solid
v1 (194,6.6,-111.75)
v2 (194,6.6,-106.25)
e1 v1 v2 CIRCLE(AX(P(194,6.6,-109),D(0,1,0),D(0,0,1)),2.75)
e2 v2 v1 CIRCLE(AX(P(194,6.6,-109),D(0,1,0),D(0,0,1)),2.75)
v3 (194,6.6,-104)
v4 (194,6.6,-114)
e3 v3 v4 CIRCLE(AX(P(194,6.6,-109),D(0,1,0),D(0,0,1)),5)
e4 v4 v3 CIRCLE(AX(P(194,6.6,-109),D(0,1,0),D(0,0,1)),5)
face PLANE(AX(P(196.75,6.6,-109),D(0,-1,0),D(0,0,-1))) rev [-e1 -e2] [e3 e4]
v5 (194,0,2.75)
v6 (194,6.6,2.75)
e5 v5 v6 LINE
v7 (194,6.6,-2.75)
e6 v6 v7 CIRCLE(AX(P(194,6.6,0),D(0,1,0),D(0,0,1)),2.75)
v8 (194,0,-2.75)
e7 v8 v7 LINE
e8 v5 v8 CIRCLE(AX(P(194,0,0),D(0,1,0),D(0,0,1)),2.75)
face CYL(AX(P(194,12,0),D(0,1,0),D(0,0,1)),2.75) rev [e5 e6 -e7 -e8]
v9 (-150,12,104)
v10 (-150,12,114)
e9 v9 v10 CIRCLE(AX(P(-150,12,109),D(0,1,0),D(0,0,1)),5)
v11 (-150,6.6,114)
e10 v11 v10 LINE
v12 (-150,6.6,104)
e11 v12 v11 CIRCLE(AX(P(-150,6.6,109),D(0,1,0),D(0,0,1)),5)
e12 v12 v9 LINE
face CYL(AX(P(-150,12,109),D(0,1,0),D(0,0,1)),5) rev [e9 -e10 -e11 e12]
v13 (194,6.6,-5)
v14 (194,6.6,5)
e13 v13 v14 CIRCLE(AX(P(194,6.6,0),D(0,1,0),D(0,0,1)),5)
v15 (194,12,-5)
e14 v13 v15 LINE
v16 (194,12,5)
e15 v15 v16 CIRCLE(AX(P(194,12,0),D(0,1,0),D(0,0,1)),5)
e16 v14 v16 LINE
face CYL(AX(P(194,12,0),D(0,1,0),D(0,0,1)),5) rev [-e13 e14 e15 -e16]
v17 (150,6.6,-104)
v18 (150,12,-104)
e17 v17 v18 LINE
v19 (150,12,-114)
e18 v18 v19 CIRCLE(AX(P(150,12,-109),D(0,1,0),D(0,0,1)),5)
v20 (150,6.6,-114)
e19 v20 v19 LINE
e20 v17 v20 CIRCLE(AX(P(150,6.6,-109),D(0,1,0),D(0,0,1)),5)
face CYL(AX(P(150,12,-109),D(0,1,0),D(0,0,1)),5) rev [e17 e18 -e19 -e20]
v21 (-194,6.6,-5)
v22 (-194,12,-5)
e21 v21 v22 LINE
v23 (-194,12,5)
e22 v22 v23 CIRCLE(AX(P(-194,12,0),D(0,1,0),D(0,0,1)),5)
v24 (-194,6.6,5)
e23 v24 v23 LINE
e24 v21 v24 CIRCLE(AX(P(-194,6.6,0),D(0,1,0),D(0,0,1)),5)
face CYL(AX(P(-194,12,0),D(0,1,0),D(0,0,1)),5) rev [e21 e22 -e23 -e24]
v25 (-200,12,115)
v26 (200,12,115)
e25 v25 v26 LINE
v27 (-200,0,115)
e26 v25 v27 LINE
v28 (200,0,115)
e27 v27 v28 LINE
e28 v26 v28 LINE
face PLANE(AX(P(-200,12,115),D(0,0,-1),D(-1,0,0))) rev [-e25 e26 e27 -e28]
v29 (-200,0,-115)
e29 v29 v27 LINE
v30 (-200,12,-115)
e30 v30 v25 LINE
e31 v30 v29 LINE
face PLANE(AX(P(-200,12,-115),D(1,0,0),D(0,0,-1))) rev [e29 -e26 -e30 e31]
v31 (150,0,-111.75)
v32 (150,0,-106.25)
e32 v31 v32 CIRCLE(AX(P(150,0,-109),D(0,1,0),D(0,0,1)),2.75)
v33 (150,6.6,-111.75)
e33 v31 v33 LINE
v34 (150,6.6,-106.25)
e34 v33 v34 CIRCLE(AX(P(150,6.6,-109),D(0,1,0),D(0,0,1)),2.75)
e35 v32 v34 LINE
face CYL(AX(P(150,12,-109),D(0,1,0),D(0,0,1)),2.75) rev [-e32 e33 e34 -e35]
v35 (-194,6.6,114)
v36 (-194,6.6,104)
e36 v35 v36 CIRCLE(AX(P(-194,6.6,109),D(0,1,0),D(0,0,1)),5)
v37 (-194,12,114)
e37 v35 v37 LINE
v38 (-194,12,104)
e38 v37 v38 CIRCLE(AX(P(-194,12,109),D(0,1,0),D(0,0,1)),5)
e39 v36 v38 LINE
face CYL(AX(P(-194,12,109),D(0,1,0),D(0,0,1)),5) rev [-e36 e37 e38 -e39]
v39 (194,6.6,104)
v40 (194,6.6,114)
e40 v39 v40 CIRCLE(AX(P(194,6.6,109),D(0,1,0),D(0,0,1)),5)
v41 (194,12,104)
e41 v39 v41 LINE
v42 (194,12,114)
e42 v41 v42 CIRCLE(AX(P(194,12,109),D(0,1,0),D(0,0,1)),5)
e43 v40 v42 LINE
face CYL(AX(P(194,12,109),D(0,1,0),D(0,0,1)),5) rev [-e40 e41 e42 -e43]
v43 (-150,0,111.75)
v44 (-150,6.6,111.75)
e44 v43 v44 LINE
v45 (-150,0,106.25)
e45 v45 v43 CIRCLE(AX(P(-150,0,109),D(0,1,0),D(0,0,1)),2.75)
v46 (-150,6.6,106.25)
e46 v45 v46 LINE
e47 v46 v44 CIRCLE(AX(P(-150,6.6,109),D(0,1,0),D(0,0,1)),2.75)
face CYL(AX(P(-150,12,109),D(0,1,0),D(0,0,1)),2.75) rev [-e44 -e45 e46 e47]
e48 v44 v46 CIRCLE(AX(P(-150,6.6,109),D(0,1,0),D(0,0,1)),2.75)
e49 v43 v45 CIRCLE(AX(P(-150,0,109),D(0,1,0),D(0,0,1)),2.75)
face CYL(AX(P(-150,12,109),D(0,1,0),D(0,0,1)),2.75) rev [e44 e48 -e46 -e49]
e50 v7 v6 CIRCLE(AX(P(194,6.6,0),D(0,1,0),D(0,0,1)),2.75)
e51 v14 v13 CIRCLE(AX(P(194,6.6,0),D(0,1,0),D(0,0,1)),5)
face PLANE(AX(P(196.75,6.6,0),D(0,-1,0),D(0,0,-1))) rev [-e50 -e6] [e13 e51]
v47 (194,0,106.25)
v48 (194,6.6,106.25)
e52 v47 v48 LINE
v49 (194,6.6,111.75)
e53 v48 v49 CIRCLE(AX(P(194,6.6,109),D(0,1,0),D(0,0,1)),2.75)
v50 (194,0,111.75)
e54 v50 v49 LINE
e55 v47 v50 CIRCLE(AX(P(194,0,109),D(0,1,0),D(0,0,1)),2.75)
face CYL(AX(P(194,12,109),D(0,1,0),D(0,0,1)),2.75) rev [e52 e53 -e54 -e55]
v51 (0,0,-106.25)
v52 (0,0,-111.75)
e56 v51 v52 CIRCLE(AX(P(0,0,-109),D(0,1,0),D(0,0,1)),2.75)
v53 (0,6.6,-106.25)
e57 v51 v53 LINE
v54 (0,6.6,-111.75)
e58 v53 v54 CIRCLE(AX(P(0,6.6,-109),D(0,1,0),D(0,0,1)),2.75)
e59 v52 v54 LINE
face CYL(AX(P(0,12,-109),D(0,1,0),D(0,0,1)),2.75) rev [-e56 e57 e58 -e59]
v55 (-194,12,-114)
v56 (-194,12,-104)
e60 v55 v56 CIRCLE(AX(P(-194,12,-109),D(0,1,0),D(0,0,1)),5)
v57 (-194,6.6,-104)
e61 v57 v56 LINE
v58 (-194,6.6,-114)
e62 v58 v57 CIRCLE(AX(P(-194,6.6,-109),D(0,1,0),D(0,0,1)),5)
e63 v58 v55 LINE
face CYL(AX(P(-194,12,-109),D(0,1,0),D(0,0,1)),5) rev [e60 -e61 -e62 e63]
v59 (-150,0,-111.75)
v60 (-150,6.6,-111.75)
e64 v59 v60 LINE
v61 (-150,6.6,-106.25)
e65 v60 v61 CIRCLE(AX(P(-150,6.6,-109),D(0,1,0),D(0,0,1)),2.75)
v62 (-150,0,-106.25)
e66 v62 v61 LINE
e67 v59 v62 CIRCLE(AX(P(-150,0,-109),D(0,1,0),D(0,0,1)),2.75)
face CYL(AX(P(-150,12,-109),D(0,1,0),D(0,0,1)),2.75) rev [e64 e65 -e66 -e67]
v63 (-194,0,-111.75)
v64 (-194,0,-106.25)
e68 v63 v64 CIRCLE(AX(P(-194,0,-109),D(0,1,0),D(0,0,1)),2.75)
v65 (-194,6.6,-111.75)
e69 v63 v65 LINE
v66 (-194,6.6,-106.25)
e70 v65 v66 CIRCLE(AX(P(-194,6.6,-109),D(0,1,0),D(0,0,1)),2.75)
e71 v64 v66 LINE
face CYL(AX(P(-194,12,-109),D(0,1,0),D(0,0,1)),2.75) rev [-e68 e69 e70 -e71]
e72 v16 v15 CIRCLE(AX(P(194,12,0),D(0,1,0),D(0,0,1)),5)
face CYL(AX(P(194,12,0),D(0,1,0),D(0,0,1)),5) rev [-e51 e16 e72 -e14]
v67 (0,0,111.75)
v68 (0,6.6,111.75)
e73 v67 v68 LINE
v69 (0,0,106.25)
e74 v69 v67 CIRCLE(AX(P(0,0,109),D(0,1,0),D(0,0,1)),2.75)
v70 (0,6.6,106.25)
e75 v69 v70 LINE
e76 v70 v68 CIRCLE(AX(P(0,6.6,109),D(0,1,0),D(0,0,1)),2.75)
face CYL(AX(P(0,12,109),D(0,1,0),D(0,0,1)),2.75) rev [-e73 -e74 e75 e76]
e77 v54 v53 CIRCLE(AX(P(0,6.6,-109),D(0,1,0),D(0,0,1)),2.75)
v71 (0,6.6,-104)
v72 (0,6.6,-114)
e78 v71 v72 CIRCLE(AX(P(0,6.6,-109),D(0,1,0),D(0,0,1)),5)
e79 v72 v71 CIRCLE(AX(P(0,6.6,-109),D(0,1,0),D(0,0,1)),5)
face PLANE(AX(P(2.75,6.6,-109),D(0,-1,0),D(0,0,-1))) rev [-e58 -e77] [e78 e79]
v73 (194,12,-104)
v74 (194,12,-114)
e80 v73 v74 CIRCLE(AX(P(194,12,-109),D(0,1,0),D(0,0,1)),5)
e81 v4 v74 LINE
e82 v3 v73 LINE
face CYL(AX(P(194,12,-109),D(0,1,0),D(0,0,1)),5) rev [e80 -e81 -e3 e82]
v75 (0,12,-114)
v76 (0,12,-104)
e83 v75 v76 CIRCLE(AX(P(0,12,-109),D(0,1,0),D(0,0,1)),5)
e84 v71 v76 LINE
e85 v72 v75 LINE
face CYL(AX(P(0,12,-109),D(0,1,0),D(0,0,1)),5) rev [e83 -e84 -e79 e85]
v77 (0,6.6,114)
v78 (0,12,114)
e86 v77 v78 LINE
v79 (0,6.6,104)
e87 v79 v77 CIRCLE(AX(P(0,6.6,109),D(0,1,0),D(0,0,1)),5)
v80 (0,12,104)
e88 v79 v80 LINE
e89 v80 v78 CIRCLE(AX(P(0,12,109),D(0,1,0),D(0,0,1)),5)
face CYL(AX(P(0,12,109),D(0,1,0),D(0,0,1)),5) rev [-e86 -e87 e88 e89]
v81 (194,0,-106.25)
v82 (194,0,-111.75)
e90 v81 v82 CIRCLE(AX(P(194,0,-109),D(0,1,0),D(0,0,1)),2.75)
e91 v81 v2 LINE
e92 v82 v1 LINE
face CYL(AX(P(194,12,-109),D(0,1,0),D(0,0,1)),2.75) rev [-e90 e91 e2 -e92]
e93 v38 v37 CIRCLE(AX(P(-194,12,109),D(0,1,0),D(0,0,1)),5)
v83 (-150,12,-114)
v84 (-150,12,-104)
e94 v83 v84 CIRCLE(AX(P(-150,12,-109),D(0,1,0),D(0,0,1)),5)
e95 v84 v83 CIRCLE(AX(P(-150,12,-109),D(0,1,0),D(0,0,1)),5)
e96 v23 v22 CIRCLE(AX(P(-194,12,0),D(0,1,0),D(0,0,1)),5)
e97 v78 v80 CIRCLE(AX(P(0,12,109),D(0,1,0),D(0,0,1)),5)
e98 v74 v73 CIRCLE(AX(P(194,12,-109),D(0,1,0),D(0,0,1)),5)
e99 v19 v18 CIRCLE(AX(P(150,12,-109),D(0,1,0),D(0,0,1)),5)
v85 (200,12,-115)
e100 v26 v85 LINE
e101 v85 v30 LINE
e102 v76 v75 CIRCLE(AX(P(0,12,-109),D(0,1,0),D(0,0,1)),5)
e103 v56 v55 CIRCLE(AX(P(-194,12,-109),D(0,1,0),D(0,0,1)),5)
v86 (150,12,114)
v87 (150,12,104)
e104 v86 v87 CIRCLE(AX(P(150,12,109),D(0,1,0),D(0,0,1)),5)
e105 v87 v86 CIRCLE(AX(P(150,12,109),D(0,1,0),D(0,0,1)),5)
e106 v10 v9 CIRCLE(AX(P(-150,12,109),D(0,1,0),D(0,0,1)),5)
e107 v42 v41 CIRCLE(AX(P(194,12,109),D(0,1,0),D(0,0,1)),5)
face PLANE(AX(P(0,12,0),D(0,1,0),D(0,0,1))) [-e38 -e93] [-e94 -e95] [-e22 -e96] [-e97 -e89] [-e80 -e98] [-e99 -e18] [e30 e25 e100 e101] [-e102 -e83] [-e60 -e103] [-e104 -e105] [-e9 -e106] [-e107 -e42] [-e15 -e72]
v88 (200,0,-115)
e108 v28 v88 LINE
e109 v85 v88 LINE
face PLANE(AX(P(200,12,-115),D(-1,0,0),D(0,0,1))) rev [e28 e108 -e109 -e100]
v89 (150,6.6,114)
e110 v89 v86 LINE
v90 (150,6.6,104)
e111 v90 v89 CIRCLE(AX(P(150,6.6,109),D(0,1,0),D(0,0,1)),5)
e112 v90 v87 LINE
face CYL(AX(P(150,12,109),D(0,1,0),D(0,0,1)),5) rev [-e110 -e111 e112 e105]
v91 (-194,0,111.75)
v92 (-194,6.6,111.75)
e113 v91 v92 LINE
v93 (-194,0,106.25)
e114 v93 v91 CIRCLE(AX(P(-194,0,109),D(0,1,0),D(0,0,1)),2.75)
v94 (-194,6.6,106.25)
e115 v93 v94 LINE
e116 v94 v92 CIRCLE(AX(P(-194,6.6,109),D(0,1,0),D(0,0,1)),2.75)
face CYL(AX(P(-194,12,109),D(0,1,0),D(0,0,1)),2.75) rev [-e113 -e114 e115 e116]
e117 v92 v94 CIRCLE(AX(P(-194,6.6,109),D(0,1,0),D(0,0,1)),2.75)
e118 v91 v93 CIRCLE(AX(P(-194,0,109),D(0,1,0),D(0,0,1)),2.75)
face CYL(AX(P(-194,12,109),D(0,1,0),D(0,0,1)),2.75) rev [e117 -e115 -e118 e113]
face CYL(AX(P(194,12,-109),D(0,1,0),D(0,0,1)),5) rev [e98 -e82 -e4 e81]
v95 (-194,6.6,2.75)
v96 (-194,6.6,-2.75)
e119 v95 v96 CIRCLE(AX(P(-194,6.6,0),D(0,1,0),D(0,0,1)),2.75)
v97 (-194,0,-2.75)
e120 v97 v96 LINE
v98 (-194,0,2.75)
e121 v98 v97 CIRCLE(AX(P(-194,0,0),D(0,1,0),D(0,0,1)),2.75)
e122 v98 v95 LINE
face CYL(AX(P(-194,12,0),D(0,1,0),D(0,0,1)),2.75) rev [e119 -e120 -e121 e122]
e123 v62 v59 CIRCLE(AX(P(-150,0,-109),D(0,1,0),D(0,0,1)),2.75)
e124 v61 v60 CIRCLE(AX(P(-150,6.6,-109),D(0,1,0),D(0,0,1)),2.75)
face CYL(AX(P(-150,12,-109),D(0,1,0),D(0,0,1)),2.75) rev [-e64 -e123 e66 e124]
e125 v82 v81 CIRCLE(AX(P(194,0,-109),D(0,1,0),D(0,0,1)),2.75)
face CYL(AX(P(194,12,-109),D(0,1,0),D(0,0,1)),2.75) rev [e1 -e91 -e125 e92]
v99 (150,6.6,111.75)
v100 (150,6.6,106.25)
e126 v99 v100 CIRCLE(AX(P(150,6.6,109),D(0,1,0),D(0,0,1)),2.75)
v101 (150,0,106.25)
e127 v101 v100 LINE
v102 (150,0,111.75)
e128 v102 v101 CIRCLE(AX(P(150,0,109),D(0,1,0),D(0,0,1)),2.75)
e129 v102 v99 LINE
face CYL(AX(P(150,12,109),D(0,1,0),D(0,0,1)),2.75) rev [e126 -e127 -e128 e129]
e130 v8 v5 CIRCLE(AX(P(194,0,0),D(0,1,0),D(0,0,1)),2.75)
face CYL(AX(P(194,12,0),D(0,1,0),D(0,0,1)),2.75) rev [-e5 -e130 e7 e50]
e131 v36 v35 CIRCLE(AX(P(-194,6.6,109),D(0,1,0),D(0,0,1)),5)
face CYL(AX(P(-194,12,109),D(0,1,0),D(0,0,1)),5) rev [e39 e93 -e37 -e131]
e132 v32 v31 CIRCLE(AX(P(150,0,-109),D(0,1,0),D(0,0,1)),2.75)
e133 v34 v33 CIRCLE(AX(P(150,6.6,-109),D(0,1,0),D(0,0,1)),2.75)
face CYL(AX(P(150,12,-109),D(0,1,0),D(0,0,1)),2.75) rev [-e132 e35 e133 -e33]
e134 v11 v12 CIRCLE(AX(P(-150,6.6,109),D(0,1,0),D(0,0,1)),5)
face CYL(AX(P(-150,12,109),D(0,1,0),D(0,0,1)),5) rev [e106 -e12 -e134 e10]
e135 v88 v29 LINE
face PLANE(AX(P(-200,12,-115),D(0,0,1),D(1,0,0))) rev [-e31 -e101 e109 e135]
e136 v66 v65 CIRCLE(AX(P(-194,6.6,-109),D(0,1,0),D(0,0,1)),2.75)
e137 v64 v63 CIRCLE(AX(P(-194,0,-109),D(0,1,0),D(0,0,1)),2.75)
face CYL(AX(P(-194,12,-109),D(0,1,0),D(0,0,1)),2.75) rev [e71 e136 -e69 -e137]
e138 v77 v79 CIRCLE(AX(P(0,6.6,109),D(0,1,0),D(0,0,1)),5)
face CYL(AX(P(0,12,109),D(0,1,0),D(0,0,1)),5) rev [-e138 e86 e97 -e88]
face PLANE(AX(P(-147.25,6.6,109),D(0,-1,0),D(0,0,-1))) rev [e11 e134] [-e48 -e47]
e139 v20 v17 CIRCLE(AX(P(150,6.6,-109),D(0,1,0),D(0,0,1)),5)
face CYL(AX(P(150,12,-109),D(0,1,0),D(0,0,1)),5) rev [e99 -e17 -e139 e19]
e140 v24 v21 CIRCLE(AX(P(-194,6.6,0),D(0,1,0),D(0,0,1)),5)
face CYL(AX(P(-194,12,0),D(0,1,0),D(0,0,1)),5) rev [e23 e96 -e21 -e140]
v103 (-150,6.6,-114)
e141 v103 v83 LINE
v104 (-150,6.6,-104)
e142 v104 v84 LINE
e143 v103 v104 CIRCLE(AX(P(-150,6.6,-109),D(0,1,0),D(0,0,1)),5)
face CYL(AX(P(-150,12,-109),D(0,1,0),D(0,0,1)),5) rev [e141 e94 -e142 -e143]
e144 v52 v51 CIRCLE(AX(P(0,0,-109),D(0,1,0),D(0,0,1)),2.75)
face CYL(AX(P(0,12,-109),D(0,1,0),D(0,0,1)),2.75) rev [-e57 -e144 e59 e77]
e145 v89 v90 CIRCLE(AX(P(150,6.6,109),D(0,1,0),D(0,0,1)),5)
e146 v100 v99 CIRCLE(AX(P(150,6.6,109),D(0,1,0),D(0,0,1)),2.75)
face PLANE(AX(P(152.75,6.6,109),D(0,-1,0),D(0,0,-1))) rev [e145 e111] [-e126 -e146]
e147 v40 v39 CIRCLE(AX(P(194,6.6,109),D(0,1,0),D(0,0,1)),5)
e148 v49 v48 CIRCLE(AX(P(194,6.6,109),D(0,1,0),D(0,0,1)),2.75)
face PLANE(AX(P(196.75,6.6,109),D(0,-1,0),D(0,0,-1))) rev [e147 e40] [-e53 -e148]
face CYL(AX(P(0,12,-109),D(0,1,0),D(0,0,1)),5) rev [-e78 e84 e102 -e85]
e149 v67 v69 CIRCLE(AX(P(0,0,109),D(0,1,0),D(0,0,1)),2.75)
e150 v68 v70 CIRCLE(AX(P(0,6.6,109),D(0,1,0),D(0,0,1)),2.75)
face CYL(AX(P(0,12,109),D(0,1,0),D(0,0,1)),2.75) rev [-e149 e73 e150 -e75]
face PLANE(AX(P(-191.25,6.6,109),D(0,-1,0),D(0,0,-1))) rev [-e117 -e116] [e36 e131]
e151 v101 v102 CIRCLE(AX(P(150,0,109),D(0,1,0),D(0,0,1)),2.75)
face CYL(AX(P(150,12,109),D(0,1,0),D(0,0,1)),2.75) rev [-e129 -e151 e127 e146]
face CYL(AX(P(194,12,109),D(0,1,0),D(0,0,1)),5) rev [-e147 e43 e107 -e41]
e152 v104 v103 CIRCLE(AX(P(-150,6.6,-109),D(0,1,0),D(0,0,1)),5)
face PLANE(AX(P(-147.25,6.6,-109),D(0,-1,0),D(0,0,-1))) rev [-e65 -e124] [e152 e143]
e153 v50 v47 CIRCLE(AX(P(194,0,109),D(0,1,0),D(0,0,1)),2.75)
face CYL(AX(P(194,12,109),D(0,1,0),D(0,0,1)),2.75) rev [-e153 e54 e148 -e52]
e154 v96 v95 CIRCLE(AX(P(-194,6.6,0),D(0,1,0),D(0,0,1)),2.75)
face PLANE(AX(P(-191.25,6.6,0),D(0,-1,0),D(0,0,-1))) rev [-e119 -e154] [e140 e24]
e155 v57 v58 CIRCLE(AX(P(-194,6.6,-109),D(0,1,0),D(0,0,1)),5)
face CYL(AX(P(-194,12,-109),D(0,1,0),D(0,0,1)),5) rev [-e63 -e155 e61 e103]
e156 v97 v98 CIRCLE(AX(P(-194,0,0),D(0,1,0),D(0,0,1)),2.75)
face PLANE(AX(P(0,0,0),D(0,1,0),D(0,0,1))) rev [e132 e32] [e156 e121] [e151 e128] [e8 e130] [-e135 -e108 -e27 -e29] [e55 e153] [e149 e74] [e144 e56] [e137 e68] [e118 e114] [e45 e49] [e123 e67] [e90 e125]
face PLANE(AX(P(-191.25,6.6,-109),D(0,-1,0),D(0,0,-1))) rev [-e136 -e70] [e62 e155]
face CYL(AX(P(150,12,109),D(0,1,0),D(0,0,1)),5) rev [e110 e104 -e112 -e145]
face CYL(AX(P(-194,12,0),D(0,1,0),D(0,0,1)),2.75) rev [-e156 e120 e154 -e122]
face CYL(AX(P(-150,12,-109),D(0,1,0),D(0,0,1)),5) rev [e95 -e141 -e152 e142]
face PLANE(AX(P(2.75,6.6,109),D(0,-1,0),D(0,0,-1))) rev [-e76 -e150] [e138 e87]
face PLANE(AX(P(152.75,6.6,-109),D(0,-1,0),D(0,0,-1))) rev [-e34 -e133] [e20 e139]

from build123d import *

# Parameters (mm, degrees)
SKETCH1_W                                           = 400
SKETCH1_H                                           = 230
BOSS_EXTRUDE1_DEPTH                                 = 12
CBORE_FOR_M5_HEX_SOCKET_HEAD_CAP_SCREW1_D           = 5.5
CBORE_FOR_M5_HEX_SOCKET_HEAD_CAP_SCREW1_DEPTH       = 24.5
CBORE_FOR_M5_HEX_SOCKET_HEAD_CAP_SCREW1_CBORE_D     = 10
CBORE_FOR_M5_HEX_SOCKET_HEAD_CAP_SCREW1_CBORE_DEPTH = 5.4
CBORE_FOR_M5_HEX_SOCKET_HEAD_CAP_SCREW1_TIP         = 1.652366702


with BuildPart() as part:
    # Sketch1 → Boss-Extrude1 (new body)
    with BuildSketch(Plane(origin=(0, 0, 0), x_dir=(1, 0, 0), z_dir=(0, 1, 0))):
        Rectangle(SKETCH1_W, SKETCH1_H)
    extrude(amount=BOSS_EXTRUDE1_DEPTH)

    # CBORE for M5 Hex Socket Head Cap Screw1
    with Locations(Plane(origin=(0, 12, 0), x_dir=(1, 0, 0), z_dir=(0, 1, 0))):
        with Locations((-194, 109), (-150, 109), (150, 109), (194, 109), (194, 0), (194, -109), (150, -109), (-150, -109), (-194, -109), (-194, 0), (0, 109), (0, -109)):
            CounterBoreHole(CBORE_FOR_M5_HEX_SOCKET_HEAD_CAP_SCREW1_D / 2, CBORE_FOR_M5_HEX_SOCKET_HEAD_CAP_SCREW1_CBORE_D / 2, CBORE_FOR_M5_HEX_SOCKET_HEAD_CAP_SCREW1_CBORE_DEPTH, depth=CBORE_FOR_M5_HEX_SOCKET_HEAD_CAP_SCREW1_DEPTH)
            with Locations((0, 0, -(CBORE_FOR_M5_HEX_SOCKET_HEAD_CAP_SCREW1_DEPTH + CBORE_FOR_M5_HEX_SOCKET_HEAD_CAP_SCREW1_TIP / 2))):  # 118° drill point
                Cone(0, CBORE_FOR_M5_HEX_SOCKET_HEAD_CAP_SCREW1_D / 2, CBORE_FOR_M5_HEX_SOCKET_HEAD_CAP_SCREW1_TIP, mode=Mode.SUBTRACT)


solid = part.part
